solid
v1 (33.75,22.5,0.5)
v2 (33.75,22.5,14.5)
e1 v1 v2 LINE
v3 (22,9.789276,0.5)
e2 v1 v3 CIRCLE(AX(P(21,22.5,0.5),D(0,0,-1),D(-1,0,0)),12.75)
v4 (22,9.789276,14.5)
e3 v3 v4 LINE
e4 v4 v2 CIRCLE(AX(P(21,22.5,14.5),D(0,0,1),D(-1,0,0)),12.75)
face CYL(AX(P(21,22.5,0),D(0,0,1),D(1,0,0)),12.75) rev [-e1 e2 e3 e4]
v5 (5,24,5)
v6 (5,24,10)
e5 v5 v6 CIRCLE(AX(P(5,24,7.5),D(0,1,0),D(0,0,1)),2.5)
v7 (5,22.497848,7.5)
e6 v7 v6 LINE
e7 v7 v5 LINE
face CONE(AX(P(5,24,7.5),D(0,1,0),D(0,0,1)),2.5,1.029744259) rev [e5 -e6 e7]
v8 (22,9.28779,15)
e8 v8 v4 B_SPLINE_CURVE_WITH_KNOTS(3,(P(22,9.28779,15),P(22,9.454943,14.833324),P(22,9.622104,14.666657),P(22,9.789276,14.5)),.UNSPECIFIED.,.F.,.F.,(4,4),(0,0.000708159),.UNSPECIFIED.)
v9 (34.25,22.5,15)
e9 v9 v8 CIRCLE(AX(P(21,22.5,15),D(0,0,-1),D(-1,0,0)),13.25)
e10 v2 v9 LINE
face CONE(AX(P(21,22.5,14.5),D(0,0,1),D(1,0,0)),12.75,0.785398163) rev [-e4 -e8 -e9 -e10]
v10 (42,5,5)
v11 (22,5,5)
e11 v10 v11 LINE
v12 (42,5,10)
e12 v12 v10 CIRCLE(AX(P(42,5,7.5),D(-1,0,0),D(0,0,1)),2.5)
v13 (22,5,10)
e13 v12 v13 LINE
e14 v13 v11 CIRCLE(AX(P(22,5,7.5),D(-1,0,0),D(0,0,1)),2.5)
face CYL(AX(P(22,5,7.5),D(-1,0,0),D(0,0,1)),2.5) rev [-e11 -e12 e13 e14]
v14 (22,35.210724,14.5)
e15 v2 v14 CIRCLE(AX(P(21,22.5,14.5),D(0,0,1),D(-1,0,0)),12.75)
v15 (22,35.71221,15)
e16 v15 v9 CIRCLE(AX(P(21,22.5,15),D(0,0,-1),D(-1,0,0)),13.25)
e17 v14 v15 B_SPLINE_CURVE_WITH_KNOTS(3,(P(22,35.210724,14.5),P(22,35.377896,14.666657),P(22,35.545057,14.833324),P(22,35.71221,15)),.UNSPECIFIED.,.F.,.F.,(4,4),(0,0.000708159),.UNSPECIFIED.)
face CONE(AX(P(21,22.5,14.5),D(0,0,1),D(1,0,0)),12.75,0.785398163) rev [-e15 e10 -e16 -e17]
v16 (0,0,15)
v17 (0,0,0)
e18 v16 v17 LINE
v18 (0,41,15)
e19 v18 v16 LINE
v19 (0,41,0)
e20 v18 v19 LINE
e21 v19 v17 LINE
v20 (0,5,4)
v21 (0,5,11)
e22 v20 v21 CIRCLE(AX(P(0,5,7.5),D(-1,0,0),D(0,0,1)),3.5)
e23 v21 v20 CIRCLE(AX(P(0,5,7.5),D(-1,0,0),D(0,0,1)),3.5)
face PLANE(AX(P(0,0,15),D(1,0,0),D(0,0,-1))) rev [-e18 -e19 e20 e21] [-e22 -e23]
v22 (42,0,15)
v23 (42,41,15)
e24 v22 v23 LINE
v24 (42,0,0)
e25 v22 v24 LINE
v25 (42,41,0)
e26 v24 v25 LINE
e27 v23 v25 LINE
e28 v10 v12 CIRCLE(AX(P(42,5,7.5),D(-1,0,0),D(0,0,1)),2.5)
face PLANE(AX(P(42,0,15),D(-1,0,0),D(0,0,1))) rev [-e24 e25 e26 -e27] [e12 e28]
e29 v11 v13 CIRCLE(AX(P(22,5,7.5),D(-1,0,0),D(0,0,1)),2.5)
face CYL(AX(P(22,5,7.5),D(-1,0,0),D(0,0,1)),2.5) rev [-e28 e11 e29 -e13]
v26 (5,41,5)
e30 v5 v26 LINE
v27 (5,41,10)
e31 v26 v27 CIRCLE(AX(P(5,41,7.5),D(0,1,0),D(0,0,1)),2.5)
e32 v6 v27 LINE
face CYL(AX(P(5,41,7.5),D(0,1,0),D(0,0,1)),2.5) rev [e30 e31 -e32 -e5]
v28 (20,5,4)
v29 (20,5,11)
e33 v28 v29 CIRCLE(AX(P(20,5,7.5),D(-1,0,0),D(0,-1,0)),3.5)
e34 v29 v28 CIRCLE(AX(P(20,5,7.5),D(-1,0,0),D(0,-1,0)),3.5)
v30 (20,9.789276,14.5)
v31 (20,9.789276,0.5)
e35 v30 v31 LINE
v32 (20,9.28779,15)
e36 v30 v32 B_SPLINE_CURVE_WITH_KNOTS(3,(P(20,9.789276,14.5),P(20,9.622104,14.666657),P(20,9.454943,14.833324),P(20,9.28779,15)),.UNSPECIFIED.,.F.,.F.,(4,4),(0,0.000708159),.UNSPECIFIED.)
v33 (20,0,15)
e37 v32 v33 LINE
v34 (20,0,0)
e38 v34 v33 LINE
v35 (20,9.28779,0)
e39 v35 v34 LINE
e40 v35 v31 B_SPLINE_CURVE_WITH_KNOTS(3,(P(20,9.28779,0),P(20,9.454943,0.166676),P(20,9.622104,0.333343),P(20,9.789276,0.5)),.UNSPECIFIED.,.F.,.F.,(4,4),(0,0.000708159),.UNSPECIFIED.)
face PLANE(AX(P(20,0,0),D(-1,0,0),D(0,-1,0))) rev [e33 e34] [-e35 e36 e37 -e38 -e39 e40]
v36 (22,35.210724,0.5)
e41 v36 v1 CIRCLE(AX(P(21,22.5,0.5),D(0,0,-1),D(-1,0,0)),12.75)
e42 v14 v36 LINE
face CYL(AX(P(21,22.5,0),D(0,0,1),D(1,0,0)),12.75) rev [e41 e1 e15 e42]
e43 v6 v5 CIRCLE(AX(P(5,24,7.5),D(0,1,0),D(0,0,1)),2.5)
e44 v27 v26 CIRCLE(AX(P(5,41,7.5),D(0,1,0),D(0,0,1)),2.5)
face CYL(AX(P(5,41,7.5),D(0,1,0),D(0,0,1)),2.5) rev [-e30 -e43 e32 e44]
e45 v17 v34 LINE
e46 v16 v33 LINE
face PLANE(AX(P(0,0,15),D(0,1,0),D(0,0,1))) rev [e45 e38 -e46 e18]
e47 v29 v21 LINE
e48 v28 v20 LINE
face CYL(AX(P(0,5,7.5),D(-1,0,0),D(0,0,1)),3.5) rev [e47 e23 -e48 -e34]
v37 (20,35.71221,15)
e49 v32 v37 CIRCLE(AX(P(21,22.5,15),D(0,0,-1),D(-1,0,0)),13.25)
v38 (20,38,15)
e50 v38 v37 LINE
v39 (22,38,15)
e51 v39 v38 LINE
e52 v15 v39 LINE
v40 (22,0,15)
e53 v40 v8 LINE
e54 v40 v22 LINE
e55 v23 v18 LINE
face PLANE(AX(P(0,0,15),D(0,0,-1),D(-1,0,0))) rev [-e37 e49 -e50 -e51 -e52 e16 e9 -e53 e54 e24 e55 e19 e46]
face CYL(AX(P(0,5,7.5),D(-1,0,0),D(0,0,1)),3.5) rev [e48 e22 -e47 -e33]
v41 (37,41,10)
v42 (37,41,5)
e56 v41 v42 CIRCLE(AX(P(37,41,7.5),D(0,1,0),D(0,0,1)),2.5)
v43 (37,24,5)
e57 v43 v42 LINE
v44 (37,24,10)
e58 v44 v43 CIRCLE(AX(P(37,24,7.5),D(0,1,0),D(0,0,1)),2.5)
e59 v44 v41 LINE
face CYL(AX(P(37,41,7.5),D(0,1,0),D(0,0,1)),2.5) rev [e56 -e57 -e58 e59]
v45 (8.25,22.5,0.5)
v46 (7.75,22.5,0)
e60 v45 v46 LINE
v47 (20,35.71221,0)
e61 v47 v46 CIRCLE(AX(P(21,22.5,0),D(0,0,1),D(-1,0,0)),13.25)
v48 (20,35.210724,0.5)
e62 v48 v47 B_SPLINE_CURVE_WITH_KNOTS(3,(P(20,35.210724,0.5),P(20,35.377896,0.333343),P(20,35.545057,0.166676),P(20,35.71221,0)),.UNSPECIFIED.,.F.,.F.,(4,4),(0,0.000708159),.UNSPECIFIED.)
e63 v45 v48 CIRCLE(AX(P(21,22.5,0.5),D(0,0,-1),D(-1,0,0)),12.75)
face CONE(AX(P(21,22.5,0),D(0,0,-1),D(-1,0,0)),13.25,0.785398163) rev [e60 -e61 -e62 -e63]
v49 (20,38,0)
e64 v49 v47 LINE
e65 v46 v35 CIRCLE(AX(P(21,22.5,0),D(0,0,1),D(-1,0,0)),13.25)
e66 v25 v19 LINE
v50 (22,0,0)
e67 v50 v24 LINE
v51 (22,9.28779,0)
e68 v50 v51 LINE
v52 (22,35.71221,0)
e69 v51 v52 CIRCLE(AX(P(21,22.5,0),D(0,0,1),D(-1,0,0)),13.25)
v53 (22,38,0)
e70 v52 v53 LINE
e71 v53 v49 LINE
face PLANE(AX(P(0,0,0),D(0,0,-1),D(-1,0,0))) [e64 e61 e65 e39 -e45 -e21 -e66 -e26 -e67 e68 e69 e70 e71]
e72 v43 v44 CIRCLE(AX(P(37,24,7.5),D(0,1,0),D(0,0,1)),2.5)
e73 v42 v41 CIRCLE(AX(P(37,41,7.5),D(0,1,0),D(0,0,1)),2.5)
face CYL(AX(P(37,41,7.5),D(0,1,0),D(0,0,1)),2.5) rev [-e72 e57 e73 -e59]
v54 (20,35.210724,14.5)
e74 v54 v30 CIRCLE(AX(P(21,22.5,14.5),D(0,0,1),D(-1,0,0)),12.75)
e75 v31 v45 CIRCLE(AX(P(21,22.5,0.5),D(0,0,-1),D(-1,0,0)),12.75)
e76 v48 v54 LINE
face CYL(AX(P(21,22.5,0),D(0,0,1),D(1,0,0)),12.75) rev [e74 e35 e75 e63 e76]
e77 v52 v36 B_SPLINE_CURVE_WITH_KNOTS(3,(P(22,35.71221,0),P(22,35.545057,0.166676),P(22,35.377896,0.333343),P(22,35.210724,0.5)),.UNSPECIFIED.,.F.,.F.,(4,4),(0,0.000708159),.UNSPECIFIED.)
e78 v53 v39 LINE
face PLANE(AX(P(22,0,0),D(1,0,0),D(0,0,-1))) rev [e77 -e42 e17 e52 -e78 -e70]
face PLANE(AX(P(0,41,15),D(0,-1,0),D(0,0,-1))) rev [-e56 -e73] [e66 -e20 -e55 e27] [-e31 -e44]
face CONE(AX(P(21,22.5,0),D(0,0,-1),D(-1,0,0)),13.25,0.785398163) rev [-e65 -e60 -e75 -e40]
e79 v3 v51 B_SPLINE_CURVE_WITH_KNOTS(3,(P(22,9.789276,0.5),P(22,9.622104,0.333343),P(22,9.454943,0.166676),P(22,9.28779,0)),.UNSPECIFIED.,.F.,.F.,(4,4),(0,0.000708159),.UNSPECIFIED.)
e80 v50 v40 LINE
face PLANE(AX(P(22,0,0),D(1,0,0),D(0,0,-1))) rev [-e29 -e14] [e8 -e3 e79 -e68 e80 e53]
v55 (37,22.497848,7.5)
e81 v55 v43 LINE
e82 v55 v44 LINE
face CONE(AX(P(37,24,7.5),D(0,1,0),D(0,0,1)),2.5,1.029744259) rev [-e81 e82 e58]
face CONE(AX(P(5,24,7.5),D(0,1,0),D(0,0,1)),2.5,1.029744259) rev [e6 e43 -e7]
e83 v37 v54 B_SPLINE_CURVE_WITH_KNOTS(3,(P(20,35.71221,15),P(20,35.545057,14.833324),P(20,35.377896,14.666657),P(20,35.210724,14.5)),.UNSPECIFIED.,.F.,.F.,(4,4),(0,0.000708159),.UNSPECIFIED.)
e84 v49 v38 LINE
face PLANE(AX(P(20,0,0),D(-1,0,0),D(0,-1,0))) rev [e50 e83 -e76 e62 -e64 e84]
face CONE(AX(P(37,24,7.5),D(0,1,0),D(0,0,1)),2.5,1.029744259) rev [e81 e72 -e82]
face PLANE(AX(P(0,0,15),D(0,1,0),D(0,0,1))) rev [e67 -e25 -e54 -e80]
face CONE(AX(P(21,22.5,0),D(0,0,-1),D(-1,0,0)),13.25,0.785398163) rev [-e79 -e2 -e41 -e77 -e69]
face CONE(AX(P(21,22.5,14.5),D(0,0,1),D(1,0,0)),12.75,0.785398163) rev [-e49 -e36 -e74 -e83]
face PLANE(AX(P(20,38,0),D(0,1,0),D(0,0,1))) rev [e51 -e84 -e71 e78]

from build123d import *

# Parameters (mm, degrees)
SKETCH_1_W                = 42
SKETCH_1_H                = 41
EXTRUDE_1_DEPTH           = 15
SKETCH_2_R                = 12.75
CUT_EXTRUDE_1_DEPTH       = 15
SKETCH_3_W                = 2
SKETCH_3_H                = 38
CUT_EXTRUDE_2_DEPTH       = 15
HOLE_WIZARD_M6_1_D        = 5
HOLE_WIZARD_M6_1_DEPTH    = 17
HOLE_WIZARD_M6_1_TIP      = 1.502151548
HOLE_WIZARD_7_0_7_1_D     = 7
HOLE_WIZARD_7_0_7_1_DEPTH = 20
HOLE_WIZARD_M6_2_D        = 5
CHAMFER_1_SIZE            = 0.5
CHAMFER_2_SIZE            = 0.5


with BuildPart() as part:
    # 草图1 → 凸台-拉伸1 (new body)
    with BuildSketch(Plane.XY):
        with Locations((21, 20.5)):
            Rectangle(SKETCH_1_W, SKETCH_1_H)
    extrude(amount=EXTRUDE_1_DEPTH)

    # 草图2 → 切除-拉伸1 (cut)
    with BuildSketch(Plane.XY.offset(15)):
        with Locations((21, 22.5)):
            Circle(SKETCH_2_R)
    extrude(amount=-CUT_EXTRUDE_1_DEPTH, mode=Mode.SUBTRACT)

    # 草图3 → 切除-拉伸2 (cut)
    with BuildSketch(Plane.XY.offset(15)):
        with Locations((21, 19)):
            Rectangle(SKETCH_3_W, SKETCH_3_H)
    extrude(amount=-CUT_EXTRUDE_2_DEPTH, mode=Mode.SUBTRACT)

    # M6 螺纹孔1
    with Locations(Plane(origin=(0, 41, 0), x_dir=(1, 0, 0), z_dir=(0, 1, 0))):
        with Locations((5, -7.5), (37, -7.5)):
            Hole(HOLE_WIZARD_M6_1_D / 2, depth=HOLE_WIZARD_M6_1_DEPTH)
            with Locations((0, 0, -(HOLE_WIZARD_M6_1_DEPTH + HOLE_WIZARD_M6_1_TIP / 2))):  # 118° drill point
                Cone(0, HOLE_WIZARD_M6_1_D / 2, HOLE_WIZARD_M6_1_TIP, mode=Mode.SUBTRACT)

    # Ø7.0 (7) 直径孔1
    with Locations(Plane.ZY):
        with Locations((7.5, 5)):
            Hole(HOLE_WIZARD_7_0_7_1_D / 2, depth=HOLE_WIZARD_7_0_7_1_DEPTH)

    # M6 螺纹孔2 (through all)
    with Locations(Plane.ZY.offset(-22)):
        with Locations((7.5, 5)):
            Hole(HOLE_WIZARD_M6_2_D / 2)

    # 倒角1
    chamfer_1_edges = [part.edges().sort_by_distance(p)[0] for p in [
        (33.75, 22.5, 0),
        (33.75, 22.5, 15),
    ]]
    chamfer(chamfer_1_edges, length=CHAMFER_1_SIZE)

    # 倒角2
    chamfer_2_edges = [part.edges().sort_by_distance(p)[0] for p in [
        (8.25, 22.5, 0),
        (8.25, 22.5, 15),
    ]]
    chamfer(chamfer_2_edges, length=CHAMFER_2_SIZE)


solid = part.part
